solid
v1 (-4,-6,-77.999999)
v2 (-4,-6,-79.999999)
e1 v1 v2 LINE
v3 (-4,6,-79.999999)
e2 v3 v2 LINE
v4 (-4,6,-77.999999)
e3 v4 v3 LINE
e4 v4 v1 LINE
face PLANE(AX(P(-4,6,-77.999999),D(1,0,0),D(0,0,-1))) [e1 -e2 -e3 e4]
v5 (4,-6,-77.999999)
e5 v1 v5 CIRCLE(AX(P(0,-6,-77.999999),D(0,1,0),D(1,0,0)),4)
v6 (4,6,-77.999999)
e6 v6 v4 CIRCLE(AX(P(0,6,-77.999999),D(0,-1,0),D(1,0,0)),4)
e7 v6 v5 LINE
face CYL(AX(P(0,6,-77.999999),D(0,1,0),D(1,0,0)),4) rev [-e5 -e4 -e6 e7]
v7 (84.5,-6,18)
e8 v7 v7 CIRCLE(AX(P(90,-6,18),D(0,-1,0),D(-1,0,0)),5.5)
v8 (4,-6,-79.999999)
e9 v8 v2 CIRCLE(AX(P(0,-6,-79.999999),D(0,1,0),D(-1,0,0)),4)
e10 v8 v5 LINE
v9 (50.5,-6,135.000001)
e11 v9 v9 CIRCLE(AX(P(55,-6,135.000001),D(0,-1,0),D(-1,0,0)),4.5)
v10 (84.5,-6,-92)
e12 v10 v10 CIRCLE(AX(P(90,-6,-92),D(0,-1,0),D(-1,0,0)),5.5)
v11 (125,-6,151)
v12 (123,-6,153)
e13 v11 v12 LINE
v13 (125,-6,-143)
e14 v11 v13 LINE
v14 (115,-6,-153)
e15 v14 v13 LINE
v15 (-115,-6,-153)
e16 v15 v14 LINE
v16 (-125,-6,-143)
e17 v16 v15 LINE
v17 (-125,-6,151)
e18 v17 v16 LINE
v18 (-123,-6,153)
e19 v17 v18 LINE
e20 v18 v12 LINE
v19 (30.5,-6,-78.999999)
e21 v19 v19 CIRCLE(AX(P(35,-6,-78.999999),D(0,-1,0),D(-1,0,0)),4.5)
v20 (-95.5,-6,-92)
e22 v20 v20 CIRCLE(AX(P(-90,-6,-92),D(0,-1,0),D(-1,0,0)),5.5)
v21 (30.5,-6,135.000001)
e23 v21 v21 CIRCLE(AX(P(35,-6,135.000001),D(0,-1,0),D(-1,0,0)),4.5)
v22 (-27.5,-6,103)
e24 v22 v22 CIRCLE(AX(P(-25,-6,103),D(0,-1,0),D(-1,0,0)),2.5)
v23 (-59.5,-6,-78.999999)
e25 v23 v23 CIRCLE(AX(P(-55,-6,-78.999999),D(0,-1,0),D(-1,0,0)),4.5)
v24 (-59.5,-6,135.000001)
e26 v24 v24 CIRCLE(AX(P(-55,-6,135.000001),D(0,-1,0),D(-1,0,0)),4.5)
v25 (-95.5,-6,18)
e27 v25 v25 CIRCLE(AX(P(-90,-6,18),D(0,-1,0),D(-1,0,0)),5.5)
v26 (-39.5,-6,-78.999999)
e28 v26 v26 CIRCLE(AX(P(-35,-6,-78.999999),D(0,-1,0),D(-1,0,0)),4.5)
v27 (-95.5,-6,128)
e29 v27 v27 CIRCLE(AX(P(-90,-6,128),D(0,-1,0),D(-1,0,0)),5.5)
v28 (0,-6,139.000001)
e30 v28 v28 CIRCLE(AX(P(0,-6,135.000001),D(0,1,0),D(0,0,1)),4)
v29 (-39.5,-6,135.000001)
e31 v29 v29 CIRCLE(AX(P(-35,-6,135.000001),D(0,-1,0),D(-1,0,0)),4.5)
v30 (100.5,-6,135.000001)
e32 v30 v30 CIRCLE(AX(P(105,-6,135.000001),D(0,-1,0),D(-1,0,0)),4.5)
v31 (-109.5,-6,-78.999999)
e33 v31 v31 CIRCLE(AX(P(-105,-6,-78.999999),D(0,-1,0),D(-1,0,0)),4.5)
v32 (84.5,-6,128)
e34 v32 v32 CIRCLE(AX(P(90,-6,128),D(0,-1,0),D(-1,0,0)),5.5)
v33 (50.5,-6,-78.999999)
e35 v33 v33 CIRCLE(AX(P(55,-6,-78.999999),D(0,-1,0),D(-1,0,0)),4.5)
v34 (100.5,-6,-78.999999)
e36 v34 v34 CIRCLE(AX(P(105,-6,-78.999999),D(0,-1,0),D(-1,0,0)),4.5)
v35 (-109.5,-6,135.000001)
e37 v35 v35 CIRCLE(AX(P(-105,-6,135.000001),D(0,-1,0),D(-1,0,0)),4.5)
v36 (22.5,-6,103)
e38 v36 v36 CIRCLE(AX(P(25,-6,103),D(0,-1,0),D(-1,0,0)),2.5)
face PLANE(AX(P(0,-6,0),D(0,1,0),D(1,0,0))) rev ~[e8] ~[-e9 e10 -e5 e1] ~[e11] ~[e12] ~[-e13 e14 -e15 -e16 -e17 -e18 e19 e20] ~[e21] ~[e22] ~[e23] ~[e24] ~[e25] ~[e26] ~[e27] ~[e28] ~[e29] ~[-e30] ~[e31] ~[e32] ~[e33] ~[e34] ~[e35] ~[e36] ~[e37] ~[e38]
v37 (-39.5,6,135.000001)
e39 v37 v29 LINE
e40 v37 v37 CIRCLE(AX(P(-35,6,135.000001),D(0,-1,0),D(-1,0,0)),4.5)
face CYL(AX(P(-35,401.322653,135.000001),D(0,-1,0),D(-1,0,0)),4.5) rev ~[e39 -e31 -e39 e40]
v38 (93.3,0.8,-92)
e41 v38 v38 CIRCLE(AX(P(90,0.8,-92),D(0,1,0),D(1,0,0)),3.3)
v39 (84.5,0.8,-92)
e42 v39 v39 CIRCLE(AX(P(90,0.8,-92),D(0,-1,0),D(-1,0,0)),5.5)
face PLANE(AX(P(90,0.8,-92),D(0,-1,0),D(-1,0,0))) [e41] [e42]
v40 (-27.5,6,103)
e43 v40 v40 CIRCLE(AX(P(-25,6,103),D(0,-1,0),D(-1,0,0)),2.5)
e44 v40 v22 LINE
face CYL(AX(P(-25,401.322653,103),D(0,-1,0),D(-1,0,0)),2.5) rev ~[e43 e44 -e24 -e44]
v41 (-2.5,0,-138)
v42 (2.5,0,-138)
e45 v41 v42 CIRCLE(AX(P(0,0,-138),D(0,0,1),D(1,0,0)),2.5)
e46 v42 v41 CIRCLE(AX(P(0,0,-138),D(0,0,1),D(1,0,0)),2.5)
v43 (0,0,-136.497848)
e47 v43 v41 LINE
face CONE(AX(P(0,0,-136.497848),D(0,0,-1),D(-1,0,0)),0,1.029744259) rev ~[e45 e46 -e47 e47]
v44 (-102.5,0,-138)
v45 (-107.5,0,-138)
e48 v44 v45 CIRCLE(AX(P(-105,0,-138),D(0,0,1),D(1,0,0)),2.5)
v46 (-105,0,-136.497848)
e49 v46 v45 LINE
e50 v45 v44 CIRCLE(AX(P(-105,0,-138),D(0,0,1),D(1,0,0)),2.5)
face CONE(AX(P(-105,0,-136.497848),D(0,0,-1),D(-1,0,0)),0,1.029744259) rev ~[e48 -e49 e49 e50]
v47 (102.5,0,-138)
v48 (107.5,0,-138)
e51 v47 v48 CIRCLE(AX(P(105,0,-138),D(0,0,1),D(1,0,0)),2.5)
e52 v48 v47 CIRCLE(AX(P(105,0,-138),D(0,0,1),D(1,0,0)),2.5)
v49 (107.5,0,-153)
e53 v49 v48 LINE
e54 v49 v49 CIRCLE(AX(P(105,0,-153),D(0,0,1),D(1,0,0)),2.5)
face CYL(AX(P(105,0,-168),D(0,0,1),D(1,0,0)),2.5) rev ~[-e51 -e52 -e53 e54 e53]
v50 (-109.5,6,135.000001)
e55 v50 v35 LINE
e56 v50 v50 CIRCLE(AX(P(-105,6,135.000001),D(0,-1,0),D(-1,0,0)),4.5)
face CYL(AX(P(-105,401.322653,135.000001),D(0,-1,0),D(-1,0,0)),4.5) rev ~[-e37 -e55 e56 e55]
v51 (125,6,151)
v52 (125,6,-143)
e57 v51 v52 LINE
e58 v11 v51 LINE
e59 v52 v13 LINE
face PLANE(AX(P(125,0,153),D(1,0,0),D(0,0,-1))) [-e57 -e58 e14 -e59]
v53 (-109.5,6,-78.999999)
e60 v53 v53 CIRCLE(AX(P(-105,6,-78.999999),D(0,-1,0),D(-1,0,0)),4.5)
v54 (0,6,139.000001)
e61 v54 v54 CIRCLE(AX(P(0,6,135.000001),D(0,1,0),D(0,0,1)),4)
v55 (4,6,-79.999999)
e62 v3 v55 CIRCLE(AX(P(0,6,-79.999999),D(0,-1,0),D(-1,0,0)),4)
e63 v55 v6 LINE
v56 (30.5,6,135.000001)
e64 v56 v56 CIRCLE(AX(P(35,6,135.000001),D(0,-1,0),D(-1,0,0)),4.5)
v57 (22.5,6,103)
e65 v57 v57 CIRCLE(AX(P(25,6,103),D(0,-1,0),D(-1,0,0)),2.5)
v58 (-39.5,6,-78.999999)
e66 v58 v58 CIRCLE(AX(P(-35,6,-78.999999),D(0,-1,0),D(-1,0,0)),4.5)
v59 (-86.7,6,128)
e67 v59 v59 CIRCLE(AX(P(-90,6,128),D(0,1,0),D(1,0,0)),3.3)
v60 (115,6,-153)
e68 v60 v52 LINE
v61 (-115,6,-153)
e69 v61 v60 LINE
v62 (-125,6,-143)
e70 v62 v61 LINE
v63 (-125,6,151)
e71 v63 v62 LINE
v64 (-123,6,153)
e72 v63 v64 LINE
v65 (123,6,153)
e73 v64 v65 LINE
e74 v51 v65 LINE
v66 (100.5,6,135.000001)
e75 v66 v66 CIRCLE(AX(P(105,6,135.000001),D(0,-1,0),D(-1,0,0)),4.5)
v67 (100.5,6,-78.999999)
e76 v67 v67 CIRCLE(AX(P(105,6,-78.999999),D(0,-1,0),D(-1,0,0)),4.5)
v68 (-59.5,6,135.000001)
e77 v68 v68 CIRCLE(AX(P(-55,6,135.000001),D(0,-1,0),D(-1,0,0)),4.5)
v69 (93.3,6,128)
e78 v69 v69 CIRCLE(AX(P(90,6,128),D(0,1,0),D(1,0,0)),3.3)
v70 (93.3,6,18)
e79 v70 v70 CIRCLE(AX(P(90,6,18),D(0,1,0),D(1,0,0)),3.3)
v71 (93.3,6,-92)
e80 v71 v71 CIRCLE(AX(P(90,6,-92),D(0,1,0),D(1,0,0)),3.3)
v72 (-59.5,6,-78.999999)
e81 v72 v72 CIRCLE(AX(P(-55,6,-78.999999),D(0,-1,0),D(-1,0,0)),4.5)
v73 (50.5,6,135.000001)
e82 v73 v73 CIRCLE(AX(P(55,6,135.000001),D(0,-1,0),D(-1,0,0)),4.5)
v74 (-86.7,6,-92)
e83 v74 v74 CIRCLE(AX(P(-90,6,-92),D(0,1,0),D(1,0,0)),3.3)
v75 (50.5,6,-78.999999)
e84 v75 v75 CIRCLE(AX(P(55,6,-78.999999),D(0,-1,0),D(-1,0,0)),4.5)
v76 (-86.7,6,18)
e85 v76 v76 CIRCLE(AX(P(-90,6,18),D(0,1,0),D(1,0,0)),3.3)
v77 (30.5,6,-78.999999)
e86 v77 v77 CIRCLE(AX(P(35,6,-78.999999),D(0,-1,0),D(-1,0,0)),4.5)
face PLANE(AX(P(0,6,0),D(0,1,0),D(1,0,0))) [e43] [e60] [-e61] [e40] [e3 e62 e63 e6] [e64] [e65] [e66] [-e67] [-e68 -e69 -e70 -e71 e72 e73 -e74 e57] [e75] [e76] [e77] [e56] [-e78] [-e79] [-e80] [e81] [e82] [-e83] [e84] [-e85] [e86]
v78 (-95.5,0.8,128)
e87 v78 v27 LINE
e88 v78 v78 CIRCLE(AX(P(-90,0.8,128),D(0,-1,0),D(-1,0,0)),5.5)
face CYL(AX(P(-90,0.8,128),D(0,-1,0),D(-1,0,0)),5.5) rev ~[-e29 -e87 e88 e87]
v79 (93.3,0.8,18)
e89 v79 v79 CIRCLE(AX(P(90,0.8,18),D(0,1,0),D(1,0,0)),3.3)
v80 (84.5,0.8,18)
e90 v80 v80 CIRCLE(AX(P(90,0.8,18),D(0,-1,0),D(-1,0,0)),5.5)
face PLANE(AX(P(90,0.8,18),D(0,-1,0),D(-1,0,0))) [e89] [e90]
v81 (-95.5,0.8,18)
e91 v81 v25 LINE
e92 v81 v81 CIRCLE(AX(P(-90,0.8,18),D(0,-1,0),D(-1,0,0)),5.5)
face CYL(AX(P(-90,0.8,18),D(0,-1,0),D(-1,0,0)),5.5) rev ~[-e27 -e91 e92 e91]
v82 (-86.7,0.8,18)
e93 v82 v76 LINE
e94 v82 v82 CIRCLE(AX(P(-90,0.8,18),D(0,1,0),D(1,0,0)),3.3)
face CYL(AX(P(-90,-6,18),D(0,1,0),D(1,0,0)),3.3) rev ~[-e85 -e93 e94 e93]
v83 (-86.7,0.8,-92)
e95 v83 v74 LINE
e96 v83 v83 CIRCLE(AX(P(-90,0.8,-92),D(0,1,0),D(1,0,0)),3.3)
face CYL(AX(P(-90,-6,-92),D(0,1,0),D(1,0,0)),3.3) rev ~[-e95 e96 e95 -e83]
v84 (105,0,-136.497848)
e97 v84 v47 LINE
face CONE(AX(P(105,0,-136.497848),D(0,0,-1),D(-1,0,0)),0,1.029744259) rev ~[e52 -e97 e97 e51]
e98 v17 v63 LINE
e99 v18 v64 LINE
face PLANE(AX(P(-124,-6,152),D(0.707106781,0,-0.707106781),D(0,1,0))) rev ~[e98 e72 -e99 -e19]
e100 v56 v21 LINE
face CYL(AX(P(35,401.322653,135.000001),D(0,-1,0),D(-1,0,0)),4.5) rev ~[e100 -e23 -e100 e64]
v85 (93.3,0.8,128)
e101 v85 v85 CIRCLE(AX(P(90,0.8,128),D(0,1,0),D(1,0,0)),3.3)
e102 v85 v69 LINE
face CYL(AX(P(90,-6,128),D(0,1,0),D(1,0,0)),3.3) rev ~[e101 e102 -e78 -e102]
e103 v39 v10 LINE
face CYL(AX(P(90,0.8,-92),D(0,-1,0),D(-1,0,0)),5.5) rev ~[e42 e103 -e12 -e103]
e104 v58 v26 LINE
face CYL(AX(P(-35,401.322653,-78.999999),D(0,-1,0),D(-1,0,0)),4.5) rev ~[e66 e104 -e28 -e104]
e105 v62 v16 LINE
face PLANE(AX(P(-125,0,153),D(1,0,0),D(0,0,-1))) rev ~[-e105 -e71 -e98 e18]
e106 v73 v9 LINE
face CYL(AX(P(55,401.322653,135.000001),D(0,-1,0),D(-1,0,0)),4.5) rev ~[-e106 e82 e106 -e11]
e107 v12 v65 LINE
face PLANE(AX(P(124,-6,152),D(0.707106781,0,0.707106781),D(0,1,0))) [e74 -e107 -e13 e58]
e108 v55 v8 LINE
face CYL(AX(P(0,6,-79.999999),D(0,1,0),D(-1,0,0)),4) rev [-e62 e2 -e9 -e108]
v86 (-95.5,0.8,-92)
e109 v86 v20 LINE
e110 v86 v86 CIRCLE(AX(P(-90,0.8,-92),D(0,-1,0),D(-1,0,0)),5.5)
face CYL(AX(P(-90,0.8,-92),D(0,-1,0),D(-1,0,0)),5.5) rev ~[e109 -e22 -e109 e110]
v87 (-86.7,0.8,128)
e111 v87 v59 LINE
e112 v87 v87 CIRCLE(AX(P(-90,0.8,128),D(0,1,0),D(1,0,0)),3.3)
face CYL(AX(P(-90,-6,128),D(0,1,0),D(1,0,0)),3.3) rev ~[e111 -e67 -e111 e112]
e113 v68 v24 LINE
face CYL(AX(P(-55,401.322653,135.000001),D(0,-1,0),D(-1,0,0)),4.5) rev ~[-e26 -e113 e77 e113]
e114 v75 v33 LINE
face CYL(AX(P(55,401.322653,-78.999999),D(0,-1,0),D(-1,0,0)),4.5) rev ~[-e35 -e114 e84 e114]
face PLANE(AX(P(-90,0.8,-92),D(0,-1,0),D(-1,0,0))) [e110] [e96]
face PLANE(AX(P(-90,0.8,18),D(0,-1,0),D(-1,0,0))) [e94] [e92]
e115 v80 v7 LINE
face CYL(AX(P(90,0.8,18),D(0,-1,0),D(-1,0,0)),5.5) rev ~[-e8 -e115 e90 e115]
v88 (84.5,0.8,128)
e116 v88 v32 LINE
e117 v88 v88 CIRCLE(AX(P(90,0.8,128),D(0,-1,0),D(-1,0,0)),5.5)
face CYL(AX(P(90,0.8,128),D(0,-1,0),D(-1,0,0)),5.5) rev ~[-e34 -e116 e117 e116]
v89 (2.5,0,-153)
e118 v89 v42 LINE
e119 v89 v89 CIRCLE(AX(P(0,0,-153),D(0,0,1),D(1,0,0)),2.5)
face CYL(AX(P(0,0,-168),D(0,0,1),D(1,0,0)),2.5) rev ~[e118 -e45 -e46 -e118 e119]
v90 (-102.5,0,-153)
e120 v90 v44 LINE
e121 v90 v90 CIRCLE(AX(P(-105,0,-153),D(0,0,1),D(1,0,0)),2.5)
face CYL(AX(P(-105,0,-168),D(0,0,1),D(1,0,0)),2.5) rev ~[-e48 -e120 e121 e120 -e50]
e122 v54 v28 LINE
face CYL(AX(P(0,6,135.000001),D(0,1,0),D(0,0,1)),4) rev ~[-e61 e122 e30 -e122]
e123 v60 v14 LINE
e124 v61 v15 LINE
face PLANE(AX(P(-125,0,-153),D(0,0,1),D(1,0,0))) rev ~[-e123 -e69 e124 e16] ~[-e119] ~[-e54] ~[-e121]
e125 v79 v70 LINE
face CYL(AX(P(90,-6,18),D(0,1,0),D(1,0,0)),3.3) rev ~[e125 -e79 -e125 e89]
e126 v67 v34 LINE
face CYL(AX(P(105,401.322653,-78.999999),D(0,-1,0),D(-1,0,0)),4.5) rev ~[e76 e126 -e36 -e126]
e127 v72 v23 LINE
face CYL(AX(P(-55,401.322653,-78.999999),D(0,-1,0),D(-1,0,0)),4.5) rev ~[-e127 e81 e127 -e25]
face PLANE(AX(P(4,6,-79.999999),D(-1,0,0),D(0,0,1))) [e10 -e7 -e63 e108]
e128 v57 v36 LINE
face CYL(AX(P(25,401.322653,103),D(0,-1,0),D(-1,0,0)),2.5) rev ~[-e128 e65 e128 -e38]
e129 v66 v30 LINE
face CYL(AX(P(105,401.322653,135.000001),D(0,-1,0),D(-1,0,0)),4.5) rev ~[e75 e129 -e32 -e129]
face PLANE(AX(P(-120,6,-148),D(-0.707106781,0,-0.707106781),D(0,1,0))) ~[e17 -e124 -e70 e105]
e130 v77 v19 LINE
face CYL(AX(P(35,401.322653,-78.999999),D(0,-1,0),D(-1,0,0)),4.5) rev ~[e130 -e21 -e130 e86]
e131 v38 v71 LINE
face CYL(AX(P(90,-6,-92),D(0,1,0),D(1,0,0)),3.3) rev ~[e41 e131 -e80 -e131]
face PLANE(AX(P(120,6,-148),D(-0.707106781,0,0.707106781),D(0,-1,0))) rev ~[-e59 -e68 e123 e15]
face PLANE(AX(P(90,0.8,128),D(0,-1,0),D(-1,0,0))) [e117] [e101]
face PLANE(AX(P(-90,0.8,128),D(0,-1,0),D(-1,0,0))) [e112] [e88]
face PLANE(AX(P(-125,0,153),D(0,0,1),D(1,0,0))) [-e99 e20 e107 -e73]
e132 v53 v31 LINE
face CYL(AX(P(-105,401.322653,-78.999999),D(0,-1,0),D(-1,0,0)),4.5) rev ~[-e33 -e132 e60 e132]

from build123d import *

# Parameters (mm, degrees)
SKETCH_1_W                = 250
SKETCH_1_H                = 306
EXTRUDE_1_DEPTH           = 6
CHAMFER_1_SIZE            = 2
HOLE_WIZARD_M6_1_D        = 5
HOLE_WIZARD_M6_1_DEPTH    = 15
HOLE_WIZARD_M6_1_TIP      = 1.502151548
HOLE_WIZARD_M8_1_D        = 9
HOLE_WIZARD_1_D           = 6.6
HOLE_WIZARD_1_CBORE_D     = 11
HOLE_WIZARD_1_CBORE_DEPTH = 6.8
SKETCH_8_R                = 4
CUT_EXTRUDE_1_DEPTH       = 198.934332545
HOLE_WIZARD_M6_2_D        = 5
CHAMFER_2_SIZE            = 10


with BuildPart() as part:
    # 草图1 → 凸台-拉伸1 (new, symmetric)
    with BuildSketch(Plane(origin=(0, 0, 0), x_dir=(1, 0, 0), z_dir=(0, 1, 0))):
        Rectangle(SKETCH_1_W, SKETCH_1_H)
    extrude(amount=EXTRUDE_1_DEPTH, both=True)

    # 倒角1
    chamfer_1_edges = [part.edges().sort_by_distance(p)[0] for p in [
        (125, 0, 153),
        (-125, 0, 153),
    ]]
    chamfer(chamfer_1_edges, length=CHAMFER_1_SIZE)

    # M6 螺纹孔1
    with Locations(Plane(origin=(0, 0, -153), x_dir=(-1, 0, 0), z_dir=(0, 0, -1))):
        with Locations((-105, 0), (0, 0), (105, 0)):
            Hole(HOLE_WIZARD_M6_1_D / 2, depth=HOLE_WIZARD_M6_1_DEPTH)
            with Locations((0, 0, -(HOLE_WIZARD_M6_1_DEPTH + HOLE_WIZARD_M6_1_TIP / 2))):  # 118° drill point
                Cone(0, HOLE_WIZARD_M6_1_D / 2, HOLE_WIZARD_M6_1_TIP, mode=Mode.SUBTRACT)

    # M8 间隙孔1 (through all)
    with Locations(Plane(origin=(0, 6, 0), x_dir=(1, 0, 0), z_dir=(0, 1, 0))):
        with Locations((-105, -135.00000089), (-55, -135.00000089), (-105, 78.99999911), (-55, 78.99999911), (55, 78.99999911), (105, 78.99999911), (55, -135.00000089), (105, -135.00000089), (-35, -135.00000089), (35, -135.00000089), (-35, 78.99999911), (35, 78.99999911)):
            Hole(HOLE_WIZARD_M8_1_D / 2)

    # 打孔尺寸(%根据)内六角圆柱头螺钉的类型1 (through all)
    with Locations(Plane(origin=(0, -6, 0), x_dir=(-1, 0, 0), z_dir=(0, -1, 0))):
        with Locations((-90, -128), (-90, -18), (-90, 92), (90, 92), (90, -18), (90, -128)):
            CounterBoreHole(HOLE_WIZARD_1_D / 2, HOLE_WIZARD_1_CBORE_D / 2, HOLE_WIZARD_1_CBORE_DEPTH)

    # 草图8 → 切除-拉伸1 (cut, through all)
    with BuildSketch(Plane(origin=(0, 6, 0), x_dir=(1, 0, 0), z_dir=(0, 1, 0))):
        with Locations(Location((0, -135.00000089, 0), (0, 0, 270))):
            Circle(SKETCH_8_R)
        with BuildLine():
            Line((-4, 77.99999911), (-4, 79.99999911))
            ThreePointArc((-4, 79.99999911), (0, 83.99999911), (4, 79.99999911))
            Line((4, 79.99999911), (4, 77.99999911))
            ThreePointArc((4, 77.99999911), (0, 73.99999911), (-4, 77.99999911))
        make_face()
    extrude(amount=-CUT_EXTRUDE_1_DEPTH, mode=Mode.SUBTRACT)

    # M6 螺纹孔2 (through all)
    with Locations(Plane(origin=(0, 6, 0), x_dir=(1, 0, 0), z_dir=(0, 1, 0))):
        with Locations((25, -103), (-25, -103)):
            Hole(HOLE_WIZARD_M6_2_D / 2)

    # 倒角2
    chamfer_2_edges = [part.edges().sort_by_distance(p)[0] for p in [
        (-125, 0, -153),
        (125, 0, -153),
    ]]
    chamfer(chamfer_2_edges, length=CHAMFER_2_SIZE)


solid = part.part
